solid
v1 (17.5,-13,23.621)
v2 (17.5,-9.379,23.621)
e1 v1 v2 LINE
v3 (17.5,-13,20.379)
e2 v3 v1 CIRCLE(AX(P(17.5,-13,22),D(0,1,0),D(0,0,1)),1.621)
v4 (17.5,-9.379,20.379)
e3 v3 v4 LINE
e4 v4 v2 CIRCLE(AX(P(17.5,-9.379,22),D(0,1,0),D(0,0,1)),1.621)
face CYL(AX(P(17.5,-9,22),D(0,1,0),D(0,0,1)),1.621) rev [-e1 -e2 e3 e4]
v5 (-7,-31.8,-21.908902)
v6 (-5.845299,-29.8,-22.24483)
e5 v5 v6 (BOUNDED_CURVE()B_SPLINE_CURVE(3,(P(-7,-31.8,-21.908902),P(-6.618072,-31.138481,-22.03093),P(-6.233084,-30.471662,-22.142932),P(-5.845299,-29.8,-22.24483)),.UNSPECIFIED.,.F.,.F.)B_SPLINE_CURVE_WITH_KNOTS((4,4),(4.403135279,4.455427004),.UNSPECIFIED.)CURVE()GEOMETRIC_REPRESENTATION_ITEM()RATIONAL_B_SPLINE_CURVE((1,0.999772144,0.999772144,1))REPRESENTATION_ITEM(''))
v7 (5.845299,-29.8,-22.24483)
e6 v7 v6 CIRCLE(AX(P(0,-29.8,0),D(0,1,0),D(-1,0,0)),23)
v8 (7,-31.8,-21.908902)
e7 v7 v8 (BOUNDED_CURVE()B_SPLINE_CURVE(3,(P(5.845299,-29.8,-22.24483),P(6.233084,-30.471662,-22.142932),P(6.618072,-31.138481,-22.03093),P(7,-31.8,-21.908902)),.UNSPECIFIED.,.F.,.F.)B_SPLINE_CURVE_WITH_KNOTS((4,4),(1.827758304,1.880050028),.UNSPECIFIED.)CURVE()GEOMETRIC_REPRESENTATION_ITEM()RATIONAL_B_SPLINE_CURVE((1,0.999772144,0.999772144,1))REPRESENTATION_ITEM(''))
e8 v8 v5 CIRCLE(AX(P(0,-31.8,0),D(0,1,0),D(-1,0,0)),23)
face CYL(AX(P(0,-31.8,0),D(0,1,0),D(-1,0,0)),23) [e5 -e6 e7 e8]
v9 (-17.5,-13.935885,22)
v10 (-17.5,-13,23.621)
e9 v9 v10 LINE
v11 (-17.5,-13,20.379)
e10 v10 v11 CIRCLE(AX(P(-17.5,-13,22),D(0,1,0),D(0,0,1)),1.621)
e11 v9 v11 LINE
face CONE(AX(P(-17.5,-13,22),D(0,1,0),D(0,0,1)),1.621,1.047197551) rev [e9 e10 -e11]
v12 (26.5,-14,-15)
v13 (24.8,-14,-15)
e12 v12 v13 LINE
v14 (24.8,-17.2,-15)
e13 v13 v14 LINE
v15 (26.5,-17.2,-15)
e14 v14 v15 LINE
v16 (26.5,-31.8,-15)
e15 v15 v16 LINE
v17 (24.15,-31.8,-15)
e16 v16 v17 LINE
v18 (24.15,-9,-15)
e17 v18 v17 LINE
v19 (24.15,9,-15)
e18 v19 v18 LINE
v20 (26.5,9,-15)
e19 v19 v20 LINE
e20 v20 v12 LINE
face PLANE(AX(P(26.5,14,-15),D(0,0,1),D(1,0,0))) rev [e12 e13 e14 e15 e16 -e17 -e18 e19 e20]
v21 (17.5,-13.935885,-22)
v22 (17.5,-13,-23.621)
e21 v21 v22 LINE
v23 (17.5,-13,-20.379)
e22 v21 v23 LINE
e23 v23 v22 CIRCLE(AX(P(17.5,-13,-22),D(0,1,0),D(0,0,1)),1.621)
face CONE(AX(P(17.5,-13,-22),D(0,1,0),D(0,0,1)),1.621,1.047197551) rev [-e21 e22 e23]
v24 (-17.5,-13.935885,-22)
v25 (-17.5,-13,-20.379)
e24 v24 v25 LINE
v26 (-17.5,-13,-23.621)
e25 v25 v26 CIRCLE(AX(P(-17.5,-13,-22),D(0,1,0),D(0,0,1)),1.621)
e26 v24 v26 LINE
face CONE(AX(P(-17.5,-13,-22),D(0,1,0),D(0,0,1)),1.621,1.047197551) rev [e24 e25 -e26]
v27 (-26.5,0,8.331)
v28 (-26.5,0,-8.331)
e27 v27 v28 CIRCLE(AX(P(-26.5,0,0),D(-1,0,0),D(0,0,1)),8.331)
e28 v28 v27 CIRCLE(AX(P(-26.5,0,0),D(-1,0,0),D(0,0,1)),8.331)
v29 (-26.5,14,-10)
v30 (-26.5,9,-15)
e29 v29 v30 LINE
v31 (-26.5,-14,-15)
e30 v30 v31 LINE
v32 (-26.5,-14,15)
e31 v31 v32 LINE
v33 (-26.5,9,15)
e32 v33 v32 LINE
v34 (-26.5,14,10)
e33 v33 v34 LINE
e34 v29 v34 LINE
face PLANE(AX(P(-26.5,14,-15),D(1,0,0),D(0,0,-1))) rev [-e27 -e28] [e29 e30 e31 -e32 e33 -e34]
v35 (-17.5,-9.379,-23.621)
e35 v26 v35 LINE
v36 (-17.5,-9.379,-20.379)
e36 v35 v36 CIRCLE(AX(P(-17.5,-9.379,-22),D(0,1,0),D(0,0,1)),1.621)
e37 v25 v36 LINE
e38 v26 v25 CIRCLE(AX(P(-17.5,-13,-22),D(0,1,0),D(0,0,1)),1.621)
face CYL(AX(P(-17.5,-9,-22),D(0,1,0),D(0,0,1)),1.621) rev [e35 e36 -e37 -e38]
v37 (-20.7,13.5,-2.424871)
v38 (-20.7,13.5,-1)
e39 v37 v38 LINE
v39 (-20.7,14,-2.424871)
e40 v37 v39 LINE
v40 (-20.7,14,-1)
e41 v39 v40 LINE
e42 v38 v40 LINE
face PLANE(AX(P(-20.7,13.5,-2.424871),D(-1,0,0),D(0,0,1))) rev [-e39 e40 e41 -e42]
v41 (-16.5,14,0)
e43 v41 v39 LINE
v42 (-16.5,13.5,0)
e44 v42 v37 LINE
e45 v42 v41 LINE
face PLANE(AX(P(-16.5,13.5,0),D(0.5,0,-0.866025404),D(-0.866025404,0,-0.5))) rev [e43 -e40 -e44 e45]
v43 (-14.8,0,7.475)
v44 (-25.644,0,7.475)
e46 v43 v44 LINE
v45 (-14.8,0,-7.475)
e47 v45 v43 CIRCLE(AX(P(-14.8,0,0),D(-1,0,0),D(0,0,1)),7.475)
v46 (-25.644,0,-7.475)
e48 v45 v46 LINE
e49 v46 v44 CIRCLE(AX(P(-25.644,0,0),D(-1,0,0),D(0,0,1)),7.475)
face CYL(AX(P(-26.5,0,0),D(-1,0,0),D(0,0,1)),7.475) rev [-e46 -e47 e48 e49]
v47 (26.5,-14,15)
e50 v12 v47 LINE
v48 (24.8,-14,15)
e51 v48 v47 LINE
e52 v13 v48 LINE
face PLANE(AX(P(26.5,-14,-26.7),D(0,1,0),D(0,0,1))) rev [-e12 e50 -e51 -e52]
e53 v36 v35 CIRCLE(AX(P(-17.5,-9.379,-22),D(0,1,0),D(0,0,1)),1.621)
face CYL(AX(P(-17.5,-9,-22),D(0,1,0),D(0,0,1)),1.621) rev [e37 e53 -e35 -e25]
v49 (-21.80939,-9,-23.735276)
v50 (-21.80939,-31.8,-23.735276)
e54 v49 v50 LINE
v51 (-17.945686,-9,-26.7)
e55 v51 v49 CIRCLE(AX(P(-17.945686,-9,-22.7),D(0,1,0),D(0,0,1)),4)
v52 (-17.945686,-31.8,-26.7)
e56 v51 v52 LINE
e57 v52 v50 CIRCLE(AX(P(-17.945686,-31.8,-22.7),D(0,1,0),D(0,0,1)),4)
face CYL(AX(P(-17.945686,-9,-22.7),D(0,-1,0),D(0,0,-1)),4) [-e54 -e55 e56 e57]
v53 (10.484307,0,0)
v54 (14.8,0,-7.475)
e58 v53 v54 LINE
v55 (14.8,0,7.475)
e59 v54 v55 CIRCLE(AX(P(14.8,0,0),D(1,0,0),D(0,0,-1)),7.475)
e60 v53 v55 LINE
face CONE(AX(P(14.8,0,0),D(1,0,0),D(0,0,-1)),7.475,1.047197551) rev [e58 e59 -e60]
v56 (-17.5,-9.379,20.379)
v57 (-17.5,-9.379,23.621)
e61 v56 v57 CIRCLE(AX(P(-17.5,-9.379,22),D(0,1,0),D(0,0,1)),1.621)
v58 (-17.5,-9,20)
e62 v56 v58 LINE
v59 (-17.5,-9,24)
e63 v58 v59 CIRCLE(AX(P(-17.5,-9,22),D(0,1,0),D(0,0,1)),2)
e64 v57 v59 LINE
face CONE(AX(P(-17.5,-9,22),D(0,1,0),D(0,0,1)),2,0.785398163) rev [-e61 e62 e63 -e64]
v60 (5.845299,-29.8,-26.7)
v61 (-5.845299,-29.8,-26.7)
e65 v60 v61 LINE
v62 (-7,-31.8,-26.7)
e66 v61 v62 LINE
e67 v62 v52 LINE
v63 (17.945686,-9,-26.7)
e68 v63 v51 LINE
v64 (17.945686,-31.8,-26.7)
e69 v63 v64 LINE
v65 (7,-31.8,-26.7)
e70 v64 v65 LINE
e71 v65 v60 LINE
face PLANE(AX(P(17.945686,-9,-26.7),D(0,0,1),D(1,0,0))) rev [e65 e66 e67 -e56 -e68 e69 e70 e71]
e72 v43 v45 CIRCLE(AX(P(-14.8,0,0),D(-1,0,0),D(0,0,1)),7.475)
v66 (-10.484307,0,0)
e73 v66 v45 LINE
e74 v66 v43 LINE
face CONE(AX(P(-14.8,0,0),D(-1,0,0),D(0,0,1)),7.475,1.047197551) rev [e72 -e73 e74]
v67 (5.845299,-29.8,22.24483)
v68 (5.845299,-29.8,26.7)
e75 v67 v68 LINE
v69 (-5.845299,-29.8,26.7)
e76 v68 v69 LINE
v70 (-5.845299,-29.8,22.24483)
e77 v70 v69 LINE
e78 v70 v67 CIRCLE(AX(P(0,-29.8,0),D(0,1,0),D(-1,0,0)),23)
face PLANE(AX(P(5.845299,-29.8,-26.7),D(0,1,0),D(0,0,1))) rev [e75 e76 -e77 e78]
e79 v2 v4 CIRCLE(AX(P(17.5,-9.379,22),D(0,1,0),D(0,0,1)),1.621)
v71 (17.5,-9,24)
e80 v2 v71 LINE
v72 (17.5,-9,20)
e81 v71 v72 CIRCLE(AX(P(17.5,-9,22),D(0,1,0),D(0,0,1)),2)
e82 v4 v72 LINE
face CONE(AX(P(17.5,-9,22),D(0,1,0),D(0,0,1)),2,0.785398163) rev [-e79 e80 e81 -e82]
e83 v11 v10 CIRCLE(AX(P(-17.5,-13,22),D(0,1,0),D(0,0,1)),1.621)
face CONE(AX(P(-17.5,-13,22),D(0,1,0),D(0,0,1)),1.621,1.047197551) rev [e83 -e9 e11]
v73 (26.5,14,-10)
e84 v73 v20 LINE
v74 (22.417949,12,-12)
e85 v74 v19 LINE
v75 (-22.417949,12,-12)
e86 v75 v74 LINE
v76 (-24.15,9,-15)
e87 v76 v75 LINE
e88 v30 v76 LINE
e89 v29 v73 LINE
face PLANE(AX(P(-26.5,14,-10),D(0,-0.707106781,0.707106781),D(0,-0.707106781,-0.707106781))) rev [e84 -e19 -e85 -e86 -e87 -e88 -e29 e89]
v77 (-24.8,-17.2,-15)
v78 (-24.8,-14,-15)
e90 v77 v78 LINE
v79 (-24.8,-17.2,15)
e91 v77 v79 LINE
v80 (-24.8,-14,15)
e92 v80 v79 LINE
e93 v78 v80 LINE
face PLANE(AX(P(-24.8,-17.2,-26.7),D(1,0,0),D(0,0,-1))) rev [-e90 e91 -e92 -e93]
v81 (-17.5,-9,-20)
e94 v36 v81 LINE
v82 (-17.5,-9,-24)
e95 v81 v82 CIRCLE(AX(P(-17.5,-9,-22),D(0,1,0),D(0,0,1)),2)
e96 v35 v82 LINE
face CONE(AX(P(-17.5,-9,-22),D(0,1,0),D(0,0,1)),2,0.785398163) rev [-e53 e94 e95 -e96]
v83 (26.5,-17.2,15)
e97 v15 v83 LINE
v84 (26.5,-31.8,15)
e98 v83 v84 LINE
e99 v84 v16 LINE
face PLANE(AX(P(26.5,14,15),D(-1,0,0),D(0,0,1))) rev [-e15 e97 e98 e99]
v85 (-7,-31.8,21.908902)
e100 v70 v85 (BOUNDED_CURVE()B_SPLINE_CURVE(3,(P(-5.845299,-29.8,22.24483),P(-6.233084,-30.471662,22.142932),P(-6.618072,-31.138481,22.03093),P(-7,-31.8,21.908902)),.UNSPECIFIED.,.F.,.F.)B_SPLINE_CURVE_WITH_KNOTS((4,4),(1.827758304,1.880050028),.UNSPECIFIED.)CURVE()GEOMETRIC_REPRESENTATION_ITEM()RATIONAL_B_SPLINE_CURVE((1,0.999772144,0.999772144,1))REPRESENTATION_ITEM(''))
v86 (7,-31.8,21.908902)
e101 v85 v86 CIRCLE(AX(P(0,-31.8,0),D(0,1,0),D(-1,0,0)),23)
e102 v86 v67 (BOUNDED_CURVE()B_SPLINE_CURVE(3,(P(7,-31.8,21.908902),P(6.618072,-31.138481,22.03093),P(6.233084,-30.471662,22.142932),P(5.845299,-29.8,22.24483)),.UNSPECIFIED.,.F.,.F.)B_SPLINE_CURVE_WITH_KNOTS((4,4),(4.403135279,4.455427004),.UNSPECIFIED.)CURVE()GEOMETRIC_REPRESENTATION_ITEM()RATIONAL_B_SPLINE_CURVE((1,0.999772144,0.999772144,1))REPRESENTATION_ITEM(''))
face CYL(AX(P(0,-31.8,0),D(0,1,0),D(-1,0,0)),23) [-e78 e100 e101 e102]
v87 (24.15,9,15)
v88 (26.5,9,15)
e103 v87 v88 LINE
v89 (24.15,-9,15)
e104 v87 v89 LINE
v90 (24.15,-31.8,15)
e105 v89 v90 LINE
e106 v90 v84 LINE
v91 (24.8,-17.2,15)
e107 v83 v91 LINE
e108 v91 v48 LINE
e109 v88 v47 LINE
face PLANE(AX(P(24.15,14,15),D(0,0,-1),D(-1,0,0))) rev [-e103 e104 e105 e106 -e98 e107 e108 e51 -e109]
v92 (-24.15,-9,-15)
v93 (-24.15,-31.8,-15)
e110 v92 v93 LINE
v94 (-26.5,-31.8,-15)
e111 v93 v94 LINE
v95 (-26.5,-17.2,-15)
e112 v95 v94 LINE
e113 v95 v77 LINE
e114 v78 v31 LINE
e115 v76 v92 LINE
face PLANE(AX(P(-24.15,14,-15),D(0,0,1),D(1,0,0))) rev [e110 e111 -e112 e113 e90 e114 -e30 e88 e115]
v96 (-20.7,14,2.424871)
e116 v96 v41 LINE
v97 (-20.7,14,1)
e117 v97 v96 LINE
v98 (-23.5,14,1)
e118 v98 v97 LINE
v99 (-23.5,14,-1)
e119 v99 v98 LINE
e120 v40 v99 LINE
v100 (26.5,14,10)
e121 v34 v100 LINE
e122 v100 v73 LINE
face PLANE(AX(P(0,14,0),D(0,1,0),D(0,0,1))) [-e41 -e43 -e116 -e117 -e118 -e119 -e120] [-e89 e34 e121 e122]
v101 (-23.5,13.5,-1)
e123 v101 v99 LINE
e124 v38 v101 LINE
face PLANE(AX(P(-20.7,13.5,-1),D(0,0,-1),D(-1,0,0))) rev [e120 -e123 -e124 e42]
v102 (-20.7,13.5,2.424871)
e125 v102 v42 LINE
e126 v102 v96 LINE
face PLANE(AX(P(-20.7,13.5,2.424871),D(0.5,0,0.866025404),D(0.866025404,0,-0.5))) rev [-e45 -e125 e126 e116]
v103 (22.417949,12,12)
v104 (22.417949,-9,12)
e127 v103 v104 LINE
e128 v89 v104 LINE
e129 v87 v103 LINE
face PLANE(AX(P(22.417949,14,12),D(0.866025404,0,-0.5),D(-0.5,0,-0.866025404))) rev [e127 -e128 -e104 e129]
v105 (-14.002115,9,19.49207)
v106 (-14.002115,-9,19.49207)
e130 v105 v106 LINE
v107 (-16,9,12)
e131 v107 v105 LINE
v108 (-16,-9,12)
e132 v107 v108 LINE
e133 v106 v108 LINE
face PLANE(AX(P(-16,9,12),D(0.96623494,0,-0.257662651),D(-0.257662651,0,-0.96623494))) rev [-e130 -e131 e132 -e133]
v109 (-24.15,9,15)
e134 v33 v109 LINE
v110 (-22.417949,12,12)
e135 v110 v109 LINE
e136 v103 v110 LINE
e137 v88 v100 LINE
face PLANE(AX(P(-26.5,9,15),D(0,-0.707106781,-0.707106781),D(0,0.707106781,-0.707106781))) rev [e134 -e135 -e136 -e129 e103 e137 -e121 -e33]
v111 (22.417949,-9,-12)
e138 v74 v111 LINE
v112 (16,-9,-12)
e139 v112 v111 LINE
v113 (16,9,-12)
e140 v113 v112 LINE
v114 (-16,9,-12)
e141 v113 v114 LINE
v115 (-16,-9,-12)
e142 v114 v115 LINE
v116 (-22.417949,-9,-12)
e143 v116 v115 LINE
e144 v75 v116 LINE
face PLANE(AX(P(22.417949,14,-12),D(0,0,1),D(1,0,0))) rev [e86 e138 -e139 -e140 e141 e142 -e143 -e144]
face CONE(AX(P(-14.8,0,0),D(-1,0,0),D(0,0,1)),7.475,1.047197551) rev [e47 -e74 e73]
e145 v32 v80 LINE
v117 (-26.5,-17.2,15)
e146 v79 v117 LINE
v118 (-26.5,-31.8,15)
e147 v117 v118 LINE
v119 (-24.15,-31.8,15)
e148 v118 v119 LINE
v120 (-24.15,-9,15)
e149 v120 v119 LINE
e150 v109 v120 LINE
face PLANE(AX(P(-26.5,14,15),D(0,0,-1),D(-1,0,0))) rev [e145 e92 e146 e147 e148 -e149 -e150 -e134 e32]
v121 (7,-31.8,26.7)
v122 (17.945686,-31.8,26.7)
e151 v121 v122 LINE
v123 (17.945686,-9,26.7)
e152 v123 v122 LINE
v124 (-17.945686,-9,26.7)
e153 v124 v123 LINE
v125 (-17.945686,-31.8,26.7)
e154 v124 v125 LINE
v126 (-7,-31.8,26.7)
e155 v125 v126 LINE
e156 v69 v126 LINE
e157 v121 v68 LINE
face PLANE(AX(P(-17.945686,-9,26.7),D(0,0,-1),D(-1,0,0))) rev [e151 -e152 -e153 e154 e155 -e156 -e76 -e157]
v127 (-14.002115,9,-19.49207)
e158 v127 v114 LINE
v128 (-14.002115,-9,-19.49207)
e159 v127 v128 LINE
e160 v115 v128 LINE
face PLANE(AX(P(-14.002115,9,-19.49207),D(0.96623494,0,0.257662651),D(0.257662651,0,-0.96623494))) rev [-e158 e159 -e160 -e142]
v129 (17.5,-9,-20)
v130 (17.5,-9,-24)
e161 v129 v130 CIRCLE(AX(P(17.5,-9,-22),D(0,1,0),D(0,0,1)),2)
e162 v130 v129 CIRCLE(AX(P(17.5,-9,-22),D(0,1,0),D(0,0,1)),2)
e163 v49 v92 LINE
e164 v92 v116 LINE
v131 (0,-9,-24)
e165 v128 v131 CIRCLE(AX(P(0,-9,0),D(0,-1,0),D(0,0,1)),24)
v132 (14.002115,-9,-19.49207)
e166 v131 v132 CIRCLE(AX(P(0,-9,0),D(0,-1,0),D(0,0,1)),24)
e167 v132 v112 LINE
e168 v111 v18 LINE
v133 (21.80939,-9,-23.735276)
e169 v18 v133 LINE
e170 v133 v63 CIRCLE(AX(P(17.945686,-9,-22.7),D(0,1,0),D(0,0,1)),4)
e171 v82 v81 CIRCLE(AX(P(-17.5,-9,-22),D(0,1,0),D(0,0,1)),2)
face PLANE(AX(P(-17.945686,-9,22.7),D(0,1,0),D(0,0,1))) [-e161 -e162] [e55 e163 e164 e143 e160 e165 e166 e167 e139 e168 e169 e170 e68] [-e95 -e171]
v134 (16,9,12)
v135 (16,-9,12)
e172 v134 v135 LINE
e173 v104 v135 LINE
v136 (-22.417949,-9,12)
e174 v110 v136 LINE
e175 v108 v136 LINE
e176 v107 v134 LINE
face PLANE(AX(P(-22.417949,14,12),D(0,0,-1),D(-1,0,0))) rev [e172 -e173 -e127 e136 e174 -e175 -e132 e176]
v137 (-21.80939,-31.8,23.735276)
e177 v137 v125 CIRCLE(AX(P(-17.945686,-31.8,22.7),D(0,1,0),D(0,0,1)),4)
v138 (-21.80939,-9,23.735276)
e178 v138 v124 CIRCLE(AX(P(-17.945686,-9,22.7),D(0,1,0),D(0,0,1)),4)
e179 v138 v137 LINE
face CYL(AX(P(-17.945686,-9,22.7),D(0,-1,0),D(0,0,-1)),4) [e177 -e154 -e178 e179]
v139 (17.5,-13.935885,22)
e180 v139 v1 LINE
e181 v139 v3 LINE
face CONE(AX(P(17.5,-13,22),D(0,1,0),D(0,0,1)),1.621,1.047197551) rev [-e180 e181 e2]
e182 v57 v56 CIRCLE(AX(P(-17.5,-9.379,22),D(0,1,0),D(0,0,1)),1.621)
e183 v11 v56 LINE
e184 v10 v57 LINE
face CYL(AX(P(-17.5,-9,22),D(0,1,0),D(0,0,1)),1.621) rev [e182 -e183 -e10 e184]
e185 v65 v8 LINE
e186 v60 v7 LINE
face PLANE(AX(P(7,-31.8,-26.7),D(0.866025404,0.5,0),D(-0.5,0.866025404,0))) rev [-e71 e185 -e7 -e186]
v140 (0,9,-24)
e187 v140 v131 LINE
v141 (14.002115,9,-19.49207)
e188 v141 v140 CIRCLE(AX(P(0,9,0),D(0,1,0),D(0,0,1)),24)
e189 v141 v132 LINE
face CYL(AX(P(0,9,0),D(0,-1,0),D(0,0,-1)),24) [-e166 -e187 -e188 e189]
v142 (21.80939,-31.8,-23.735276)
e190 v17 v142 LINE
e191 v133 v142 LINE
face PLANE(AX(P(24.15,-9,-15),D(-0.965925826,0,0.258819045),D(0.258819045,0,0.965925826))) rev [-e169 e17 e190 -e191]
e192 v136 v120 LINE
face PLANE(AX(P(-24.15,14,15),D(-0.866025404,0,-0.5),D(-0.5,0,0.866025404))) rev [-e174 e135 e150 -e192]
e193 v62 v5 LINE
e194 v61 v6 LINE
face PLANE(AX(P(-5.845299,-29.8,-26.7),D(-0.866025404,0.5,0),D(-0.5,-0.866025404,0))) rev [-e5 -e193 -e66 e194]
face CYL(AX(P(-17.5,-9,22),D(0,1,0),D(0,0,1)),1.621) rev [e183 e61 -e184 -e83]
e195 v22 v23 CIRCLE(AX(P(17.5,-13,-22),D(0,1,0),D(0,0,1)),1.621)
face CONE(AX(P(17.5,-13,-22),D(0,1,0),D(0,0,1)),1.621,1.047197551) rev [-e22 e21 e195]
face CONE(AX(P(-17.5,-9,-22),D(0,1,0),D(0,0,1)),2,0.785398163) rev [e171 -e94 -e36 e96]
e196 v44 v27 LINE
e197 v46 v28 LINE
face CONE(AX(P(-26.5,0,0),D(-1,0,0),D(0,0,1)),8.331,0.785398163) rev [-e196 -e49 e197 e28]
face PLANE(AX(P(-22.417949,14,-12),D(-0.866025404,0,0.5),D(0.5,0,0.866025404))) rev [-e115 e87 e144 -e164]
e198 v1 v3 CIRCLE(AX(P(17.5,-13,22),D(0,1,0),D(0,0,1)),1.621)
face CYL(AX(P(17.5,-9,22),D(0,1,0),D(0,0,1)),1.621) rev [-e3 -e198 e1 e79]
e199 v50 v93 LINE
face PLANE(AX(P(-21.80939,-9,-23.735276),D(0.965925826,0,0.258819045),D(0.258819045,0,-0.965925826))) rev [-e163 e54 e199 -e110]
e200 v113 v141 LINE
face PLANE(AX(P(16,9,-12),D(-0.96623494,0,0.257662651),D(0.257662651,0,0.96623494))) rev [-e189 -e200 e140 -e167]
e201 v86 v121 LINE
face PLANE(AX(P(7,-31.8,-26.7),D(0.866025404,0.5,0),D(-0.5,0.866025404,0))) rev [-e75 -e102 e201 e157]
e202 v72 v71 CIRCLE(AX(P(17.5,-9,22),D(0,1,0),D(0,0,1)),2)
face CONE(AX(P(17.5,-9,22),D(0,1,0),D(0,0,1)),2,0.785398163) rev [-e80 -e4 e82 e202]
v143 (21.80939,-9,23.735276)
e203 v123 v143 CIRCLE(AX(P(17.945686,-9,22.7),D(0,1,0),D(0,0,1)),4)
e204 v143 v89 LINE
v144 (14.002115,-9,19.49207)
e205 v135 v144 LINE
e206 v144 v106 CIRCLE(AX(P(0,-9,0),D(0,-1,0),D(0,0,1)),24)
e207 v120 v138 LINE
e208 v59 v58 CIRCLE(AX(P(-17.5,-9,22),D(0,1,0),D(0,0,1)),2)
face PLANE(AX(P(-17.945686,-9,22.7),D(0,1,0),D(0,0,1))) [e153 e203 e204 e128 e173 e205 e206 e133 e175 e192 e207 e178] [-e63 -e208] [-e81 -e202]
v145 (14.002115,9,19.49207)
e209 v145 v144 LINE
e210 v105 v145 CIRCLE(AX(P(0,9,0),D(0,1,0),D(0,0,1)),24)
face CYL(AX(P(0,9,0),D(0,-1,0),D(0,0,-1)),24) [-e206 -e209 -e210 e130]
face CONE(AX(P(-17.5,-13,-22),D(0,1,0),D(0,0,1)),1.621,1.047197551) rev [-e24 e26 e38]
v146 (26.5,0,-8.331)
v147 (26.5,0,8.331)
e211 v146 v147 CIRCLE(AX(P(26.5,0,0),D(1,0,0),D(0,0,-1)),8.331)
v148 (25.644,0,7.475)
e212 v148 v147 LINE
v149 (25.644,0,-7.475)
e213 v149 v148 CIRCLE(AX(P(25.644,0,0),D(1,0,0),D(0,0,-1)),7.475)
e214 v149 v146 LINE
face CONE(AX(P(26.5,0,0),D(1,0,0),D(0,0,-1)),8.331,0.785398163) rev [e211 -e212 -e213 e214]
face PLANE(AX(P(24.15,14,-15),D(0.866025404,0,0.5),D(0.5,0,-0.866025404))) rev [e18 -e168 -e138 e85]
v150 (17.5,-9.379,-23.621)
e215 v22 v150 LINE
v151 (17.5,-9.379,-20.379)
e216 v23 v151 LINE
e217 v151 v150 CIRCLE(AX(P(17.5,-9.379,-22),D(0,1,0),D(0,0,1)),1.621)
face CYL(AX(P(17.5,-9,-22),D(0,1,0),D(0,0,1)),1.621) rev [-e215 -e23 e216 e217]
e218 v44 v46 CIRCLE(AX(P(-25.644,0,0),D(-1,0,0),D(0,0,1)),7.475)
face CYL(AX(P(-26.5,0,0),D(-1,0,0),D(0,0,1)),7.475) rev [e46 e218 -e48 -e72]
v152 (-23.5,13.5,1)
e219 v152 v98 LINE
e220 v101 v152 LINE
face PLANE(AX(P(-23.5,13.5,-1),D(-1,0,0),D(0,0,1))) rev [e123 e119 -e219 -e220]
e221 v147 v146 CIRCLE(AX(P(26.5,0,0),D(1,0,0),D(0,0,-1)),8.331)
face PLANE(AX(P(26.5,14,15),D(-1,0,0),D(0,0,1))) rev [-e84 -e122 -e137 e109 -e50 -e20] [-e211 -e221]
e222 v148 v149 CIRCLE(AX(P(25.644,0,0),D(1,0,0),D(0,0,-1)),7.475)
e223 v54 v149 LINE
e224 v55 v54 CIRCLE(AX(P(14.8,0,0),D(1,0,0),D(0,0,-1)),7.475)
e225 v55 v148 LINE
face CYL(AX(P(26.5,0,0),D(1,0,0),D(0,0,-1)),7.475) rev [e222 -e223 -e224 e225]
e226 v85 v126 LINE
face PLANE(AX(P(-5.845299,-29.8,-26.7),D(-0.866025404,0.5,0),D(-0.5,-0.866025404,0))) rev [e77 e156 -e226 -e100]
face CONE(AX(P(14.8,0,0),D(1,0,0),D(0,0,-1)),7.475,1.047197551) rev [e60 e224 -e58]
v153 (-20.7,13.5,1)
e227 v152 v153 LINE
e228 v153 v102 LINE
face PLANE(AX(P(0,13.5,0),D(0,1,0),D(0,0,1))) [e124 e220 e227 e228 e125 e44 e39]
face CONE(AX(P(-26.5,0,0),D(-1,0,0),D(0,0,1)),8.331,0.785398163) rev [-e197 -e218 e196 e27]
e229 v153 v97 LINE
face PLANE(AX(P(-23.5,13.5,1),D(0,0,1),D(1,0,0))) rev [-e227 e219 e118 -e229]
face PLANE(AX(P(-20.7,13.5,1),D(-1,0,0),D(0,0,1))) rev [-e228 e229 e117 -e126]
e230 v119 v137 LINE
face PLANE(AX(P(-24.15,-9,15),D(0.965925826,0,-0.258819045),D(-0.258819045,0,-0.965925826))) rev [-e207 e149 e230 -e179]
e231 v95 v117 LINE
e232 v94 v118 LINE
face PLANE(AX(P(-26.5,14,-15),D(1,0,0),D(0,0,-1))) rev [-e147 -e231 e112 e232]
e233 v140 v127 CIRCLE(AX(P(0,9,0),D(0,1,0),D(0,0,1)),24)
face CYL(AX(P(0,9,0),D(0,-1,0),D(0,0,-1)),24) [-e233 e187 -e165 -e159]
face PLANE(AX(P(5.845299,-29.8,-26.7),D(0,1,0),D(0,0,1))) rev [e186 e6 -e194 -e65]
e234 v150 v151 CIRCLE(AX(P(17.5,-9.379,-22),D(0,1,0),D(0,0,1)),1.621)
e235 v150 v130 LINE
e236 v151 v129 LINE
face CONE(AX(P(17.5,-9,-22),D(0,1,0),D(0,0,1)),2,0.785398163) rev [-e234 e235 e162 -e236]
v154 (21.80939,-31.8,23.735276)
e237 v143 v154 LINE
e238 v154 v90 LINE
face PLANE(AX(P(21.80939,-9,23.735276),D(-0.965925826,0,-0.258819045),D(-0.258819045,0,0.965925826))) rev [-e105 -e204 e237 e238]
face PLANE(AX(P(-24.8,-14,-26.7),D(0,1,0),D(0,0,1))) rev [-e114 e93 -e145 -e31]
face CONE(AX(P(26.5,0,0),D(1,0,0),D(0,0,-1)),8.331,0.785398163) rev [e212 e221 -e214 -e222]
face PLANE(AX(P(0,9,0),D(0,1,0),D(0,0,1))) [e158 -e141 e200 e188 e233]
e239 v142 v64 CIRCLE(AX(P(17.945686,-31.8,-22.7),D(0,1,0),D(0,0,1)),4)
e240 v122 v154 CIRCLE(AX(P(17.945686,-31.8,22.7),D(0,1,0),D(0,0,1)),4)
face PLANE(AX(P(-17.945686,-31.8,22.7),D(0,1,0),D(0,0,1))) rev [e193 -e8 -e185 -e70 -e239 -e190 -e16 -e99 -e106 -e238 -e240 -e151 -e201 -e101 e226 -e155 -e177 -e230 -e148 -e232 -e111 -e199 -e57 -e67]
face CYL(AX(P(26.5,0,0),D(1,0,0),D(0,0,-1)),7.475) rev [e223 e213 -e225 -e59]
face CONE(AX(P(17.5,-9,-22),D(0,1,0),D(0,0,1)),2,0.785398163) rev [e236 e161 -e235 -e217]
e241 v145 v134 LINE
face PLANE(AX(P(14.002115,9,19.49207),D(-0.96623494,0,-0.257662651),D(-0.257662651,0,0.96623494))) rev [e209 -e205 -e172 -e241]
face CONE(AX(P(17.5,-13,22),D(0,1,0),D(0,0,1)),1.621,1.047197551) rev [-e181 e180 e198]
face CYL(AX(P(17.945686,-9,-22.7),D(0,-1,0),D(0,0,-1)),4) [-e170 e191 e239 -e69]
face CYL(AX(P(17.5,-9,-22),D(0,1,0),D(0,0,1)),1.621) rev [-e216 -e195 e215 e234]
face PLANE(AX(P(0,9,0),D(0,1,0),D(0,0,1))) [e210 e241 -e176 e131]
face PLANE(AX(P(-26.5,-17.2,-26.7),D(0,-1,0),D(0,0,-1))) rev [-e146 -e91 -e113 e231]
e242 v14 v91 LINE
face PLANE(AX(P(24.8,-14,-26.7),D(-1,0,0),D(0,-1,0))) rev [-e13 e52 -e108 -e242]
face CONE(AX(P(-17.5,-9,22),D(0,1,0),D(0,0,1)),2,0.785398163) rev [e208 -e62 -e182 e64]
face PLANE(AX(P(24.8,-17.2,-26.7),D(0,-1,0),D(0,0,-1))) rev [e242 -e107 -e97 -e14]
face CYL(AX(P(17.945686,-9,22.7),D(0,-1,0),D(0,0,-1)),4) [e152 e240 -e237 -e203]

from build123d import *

# Parameters (mm, degrees)
EXTRUDE_1_DEPTH             = 22.8
EXTRUDE_2_DEPTH             = 45.8
CUT_EXTRUDE_1_DEPTH         = 26.5
CUT_EXTRUDE_1_DEPTH_BACK    = 26.5
EXTRUDE_3_DEPTH             = 40.8
CUT_EXTRUDE_2_DEPTH         = 26.7
CUT_EXTRUDE_2_DEPTH_BACK    = 26.7
SKETCH_5_W                  = 1.7
SKETCH_5_H                  = 3.2
CUT_EXTRUDE_3_DEPTH         = 26.7
CUT_EXTRUDE_3_DEPTH_BACK    = 26.7
SKETCH_6_W                  = 1.7
SKETCH_6_H                  = 3.2
HOLE_WIZARD_1_D             = 14.95
HOLE_WIZARD_1_DEPTH         = 11.7
HOLE_WIZARD_1_CSINK_D       = 16.662
HOLE_WIZARD_1_CSINK_ANGLE   = 90
HOLE_WIZARD_1_TIP           = 4.315693262
HOLE_WIZARD_2_D             = 14.95
HOLE_WIZARD_2_DEPTH         = 11.7
HOLE_WIZARD_2_CSINK_D       = 16.662
HOLE_WIZARD_2_CSINK_ANGLE   = 90
HOLE_WIZARD_2_TIP           = 4.315693262
PATTERN_LINEAR_1_COUNT      = 2
PATTERN_LINEAR_1_PITCH      = 44
PATTERN_LINEAR_1_COUNT_DIR2 = 2
PATTERN_LINEAR_1_PITCH_DIR2 = 35
CUT_EXTRUDE_4_DEPTH         = 0.5
CUT_EXTRUDE_5_DEPTH         = 26.7
CUT_EXTRUDE_5_DEPTH_BACK    = 26.7
SKETCH_16_W                 = 23
SKETCH_16_H                 = 2


with BuildPart() as part:
    # 草图1 → 凸台-拉伸1 (new body)
    with BuildSketch(Plane(origin=(0, -31.8, 0), x_dir=(1, 0, 0), z_dir=(0, 1, 0))):
        with BuildLine():
            Line((-24.15, -15), (-21.809389802, -23.73527618))
            ThreePointArc((-21.809389802, -23.73527618), (-20.380732213, -25.873413361), (-17.945686497, -26.7))
            Line((-17.945686497, -26.7), (17.945686497, -26.7))
            ThreePointArc((17.945686497, -26.7), (20.380732213, -25.873413361), (21.809389802, -23.73527618))
            Line((21.809389802, -23.73527618), (24.15, -15))
            Line((24.15, -15), (24.15, 15))
            Line((24.15, 15), (21.809389802, 23.73527618))
            ThreePointArc((21.809389802, 23.73527618), (20.380732213, 25.873413361), (17.945686497, 26.7))
            Line((17.945686497, 26.7), (-17.945686497, 26.7))
            ThreePointArc((-17.945686497, 26.7), (-20.380732213, 25.873413361), (-21.809389802, 23.73527618))
            Line((-21.809389802, 23.73527618), (-24.15, 15))
            Line((-24.15, 15), (-24.15, -15))
        make_face()
    extrude(amount=EXTRUDE_1_DEPTH)

    # 草图2 → 凸台-拉伸2 (add)
    with BuildSketch(Plane(origin=(0, -31.8, 0), x_dir=(1, 0, 0), z_dir=(0, 1, 0))):
        Polygon((-26.5, -15), (-24.15, -15), (-22.417949192, -12), (22.417949192, -12), (24.15, -15), (26.5, -15), (26.5, 15), (24.15, 15), (22.417949192, 12), (-22.417949192, 12), (-24.15, 15), (-26.5, 15), align=None)
    extrude(amount=EXTRUDE_2_DEPTH)

    # 草图3 → 切除-拉伸1 (cut, two sides: drawn at the far end of the back side and taken through both)
    with BuildSketch(Plane(origin=(0, 0, 0), x_dir=(0, 0, -1), z_dir=(1, 0, 0)).offset(-CUT_EXTRUDE_1_DEPTH_BACK)):
        Polygon((-26.7, 19), (-26.7, 0), (-15, 0), (-15, 9), (-10, 14), (10, 14), (15, 9), (15, 0), (26.7, 0), (26.7, 19), align=None)
    extrude(amount=CUT_EXTRUDE_1_DEPTH + CUT_EXTRUDE_1_DEPTH_BACK, mode=Mode.SUBTRACT)

    # 草图4 → 凸台-拉伸3 (add)
    with BuildSketch(Plane(origin=(0, -31.8, 0), x_dir=(1, 0, 0), z_dir=(0, 1, 0))):
        with BuildLine():
            Line((-16, -12), (-14.002114735, -19.492069745))
            ThreePointArc((-14.002114735, -19.492069745), (0, -24), (14.002114735, -19.492069745))
            Line((14.002114735, -19.492069745), (16, -12))
            Line((16, -12), (16, 12))
            Line((16, 12), (14.002114735, 19.492069745))
            ThreePointArc((14.002114735, 19.492069745), (0, 24), (-14.002114735, 19.492069745))
            Line((-14.002114735, 19.492069745), (-16, 12))
            Line((-16, 12), (-16, -12))
        make_face()
    extrude(amount=EXTRUDE_3_DEPTH)

    # 草图5 → 切除-拉伸2 (cut, two sides: drawn at the far end of the back side and taken through both)
    with BuildSketch(Plane.XY.offset(-CUT_EXTRUDE_2_DEPTH_BACK)):
        with Locations((25.65, -15.6)):
            Rectangle(SKETCH_5_W, SKETCH_5_H)
    extrude(amount=CUT_EXTRUDE_2_DEPTH + CUT_EXTRUDE_2_DEPTH_BACK, mode=Mode.SUBTRACT)

    # 草图6 → 切除-拉伸3 (cut, two sides: drawn at the far end of the back side and taken through both)
    with BuildSketch(Plane.XY.offset(-CUT_EXTRUDE_3_DEPTH_BACK)):
        with Locations((-25.65, -15.6)):
            Rectangle(SKETCH_6_W, SKETCH_6_H)
    extrude(amount=CUT_EXTRUDE_3_DEPTH + CUT_EXTRUDE_3_DEPTH_BACK, mode=Mode.SUBTRACT)

    # 孔1
    with Locations(Plane(origin=(26.5, 0, 0), x_dir=(0, 0, -1), z_dir=(1, 0, 0))):
        with Locations((0, 0)):
            CounterSinkHole(HOLE_WIZARD_1_D / 2, HOLE_WIZARD_1_CSINK_D / 2, depth=HOLE_WIZARD_1_DEPTH, counter_sink_angle=HOLE_WIZARD_1_CSINK_ANGLE)
            with Locations((0, 0, -(HOLE_WIZARD_1_DEPTH + HOLE_WIZARD_1_TIP / 2))):  # 120° drill point
                Cone(0, HOLE_WIZARD_1_D / 2, HOLE_WIZARD_1_TIP, mode=Mode.SUBTRACT)

    # 孔2
    with Locations(Plane.ZY.offset(26.5)):
        with Locations((0, 0)):
            CounterSinkHole(HOLE_WIZARD_2_D / 2, HOLE_WIZARD_2_CSINK_D / 2, depth=HOLE_WIZARD_2_DEPTH, counter_sink_angle=HOLE_WIZARD_2_CSINK_ANGLE)
            with Locations((0, 0, -(HOLE_WIZARD_2_DEPTH + HOLE_WIZARD_2_TIP / 2))):  # 120° drill point
                Cone(0, HOLE_WIZARD_2_D / 2, HOLE_WIZARD_2_TIP, mode=Mode.SUBTRACT)

    # 草图11 → 孔3 (revolve, cut)
    with BuildSketch(Plane(origin=(17.5, -9, 22), x_dir=(0, 0, 1), z_dir=(1, 0, 0))):
        Polygon((0, 0), (0, 4.935884786), (1.621, 4), (1.621, 0.379), (2, 0), align=None)
    hole_wizard_3 = revolve(axis=Axis((17.5, 5.308894879, 22), (0, -1, 0)), mode=Mode.SUBTRACT)

    # 阵列(线性)1: Hole Wizard 3 2 × 2
    with Locations(*[(-j * PATTERN_LINEAR_1_PITCH_DIR2, 0, -i * PATTERN_LINEAR_1_PITCH) for i in range(PATTERN_LINEAR_1_COUNT) for j in range(PATTERN_LINEAR_1_COUNT_DIR2) if (i, j) != (0, 0)]):
        add(hole_wizard_3, mode=Mode.SUBTRACT)

    # 草图14 → 切除-拉伸4 (cut)
    with BuildSketch(Plane(origin=(0, 14, 0), x_dir=(1, 0, 0), z_dir=(0, 1, 0))):
        Polygon((-23.5, -1), (-20.7, -1), (-20.7, -2.424871131), (-16.5, 0), (-20.7, 2.424871131), (-20.7, 1), (-23.5, 1), align=None)
    extrude(amount=-CUT_EXTRUDE_4_DEPTH, mode=Mode.SUBTRACT)

    # 草图15 → 切除-拉伸5 (cut, two sides: drawn at the far end of the back side and taken through both)
    with BuildSketch(Plane.XY.offset(-CUT_EXTRUDE_5_DEPTH_BACK)):
        Polygon((-7, -31.8), (7, -31.8), (5.845299462, -29.8), (-5.845299462, -29.8), align=None)
    extrude(amount=CUT_EXTRUDE_5_DEPTH + CUT_EXTRUDE_5_DEPTH_BACK, mode=Mode.SUBTRACT)

    # 草图16 → 旋转1 (revolve)
    with BuildSketch(Plane.XY):
        with Locations((11.5, -30.8)):
            Rectangle(SKETCH_16_W, SKETCH_16_H)
    revolve(axis=Axis((0, -31.8, 0), (0, 1, 0)))


solid = part.part
